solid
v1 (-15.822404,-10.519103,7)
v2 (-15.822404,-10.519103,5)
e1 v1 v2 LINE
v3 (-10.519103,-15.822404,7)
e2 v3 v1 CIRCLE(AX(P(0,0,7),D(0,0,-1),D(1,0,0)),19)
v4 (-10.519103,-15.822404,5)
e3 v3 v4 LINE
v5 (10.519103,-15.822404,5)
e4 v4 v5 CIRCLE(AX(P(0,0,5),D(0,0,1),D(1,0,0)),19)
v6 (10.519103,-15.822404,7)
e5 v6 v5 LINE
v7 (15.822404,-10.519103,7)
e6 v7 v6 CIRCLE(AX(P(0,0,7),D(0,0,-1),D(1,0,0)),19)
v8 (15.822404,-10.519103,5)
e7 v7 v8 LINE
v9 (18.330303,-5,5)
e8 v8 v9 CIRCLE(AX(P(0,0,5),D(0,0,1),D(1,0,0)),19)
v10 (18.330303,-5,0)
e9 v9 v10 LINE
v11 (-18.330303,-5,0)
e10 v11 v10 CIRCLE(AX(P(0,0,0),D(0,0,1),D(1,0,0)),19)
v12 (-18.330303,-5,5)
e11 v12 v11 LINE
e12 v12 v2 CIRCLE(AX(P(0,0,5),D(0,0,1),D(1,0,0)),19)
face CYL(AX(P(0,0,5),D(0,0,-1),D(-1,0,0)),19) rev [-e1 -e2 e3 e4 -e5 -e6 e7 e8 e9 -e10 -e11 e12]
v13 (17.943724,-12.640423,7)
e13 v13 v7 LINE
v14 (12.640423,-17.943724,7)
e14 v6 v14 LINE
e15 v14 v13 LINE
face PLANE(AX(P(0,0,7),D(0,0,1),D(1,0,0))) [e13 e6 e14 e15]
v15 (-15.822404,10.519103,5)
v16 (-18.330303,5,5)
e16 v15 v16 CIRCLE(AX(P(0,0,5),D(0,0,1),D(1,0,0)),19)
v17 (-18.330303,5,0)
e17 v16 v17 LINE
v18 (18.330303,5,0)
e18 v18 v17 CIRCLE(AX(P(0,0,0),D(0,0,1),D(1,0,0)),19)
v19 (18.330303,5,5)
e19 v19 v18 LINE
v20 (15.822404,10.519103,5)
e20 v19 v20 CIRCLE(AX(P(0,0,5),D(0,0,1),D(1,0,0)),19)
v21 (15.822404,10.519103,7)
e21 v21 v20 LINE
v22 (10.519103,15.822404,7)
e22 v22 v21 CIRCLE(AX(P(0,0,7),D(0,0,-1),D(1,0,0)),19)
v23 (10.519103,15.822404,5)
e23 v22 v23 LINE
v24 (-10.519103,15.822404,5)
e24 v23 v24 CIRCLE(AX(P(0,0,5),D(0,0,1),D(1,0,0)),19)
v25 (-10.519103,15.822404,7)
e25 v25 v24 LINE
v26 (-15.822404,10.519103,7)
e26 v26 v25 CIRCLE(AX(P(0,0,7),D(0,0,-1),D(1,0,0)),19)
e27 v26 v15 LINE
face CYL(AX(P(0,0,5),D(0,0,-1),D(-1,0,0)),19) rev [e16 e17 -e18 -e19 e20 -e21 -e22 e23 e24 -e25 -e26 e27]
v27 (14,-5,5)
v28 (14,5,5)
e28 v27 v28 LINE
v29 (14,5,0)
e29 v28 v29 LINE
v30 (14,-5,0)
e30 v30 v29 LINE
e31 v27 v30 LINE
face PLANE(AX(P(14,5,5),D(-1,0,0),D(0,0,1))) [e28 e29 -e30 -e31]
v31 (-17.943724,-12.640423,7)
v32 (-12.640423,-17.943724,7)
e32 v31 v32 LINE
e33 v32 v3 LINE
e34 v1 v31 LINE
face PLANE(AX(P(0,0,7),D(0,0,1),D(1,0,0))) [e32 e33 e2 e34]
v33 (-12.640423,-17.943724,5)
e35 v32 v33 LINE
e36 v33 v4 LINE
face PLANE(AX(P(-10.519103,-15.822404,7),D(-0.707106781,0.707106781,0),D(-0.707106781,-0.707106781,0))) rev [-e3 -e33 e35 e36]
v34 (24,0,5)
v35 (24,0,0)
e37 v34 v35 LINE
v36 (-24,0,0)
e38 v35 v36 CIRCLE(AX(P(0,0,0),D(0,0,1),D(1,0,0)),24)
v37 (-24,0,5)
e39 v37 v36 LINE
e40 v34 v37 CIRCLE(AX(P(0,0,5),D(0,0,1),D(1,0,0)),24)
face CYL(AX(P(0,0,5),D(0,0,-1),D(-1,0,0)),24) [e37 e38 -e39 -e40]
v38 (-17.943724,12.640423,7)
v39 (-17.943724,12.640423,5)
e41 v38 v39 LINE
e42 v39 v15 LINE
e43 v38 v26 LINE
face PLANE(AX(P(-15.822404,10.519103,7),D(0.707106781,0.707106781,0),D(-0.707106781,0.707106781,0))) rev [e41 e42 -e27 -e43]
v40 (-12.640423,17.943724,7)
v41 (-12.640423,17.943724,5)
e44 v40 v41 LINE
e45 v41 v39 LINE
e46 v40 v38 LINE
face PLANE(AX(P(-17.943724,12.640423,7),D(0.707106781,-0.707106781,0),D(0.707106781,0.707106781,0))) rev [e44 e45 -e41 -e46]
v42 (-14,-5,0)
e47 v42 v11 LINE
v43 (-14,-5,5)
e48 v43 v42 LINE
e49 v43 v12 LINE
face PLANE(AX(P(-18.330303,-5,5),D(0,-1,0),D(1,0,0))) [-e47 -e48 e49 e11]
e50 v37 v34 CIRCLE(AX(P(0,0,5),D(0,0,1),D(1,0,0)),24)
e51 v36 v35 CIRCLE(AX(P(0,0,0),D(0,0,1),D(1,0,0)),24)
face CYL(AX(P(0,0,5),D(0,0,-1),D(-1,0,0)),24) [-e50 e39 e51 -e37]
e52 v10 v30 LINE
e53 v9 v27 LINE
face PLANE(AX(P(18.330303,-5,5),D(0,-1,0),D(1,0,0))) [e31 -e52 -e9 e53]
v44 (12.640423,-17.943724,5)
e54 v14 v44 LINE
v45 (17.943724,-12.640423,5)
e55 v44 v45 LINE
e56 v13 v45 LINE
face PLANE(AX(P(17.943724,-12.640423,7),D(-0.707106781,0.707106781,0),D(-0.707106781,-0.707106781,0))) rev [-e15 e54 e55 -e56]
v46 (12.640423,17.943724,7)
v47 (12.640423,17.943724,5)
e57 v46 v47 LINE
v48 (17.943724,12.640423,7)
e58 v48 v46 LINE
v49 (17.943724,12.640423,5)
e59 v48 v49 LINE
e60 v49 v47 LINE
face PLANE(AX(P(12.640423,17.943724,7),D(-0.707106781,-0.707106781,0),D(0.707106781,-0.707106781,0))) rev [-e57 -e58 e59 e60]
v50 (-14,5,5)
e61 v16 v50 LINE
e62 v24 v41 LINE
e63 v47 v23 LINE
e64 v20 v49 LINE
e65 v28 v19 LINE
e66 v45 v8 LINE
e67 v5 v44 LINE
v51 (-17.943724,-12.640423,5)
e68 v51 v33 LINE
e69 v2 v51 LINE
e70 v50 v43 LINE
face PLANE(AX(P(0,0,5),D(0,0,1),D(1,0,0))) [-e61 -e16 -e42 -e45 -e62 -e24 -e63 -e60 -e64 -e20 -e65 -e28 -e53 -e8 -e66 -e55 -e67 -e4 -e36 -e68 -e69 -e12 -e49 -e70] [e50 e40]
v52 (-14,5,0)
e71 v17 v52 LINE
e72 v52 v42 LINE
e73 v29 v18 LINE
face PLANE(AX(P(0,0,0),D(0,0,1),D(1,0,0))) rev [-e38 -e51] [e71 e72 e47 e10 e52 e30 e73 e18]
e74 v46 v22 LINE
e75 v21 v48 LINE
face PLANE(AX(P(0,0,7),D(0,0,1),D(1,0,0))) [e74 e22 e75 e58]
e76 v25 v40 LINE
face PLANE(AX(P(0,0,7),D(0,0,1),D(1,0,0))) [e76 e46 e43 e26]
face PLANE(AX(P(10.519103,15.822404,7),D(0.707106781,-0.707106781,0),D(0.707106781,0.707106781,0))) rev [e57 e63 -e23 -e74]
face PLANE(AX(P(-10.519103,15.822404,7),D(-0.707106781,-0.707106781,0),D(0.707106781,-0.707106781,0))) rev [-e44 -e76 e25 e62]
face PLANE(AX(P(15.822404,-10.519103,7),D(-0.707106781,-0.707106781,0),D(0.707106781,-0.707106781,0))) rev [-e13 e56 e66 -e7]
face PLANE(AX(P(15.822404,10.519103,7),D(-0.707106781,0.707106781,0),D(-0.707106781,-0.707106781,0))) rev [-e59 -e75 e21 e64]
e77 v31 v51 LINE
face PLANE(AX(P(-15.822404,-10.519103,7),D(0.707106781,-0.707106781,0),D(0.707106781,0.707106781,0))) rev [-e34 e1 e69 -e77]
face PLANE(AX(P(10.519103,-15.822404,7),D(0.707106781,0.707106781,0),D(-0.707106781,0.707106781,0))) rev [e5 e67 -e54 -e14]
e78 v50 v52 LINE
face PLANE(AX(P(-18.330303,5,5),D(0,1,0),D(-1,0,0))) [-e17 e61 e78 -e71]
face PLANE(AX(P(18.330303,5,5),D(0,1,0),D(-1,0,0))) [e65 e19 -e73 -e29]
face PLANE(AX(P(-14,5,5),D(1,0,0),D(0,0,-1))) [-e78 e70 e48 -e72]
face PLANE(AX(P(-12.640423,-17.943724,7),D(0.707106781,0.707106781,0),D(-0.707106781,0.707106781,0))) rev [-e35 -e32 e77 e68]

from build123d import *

# Parameters (mm, degrees)
SKETCH_1_R      = 24
EXTRUDE_1_DEPTH = 5
EXTRUDE_2_DEPTH = 2


with BuildPart() as part:
    # 草图1 → 凸台-拉伸1 (new body)
    with BuildSketch(Plane.XY):
        Circle(SKETCH_1_R)
        with BuildLine():
            Line((-18.33030278, 5), (-14, 5))
            Line((-14, 5), (-14, -5))
            Line((-14, -5), (-18.33030278, -5))
            ThreePointArc((-18.33030278, -5), (0, -19), (18.33030278, -5))
            Line((18.33030278, -5), (14, -5))
            Line((14, -5), (14, 5))
            Line((14, 5), (18.33030278, 5))
            ThreePointArc((18.33030278, 5), (0, 19), (-18.33030278, 5))
        make_face(mode=Mode.SUBTRACT)
    extrude(amount=EXTRUDE_1_DEPTH)

    # 草图2 → 凸台-拉伸2 (add)
    with BuildSketch(Plane.XY.offset(5)):
        with BuildLine():
            Line((-15.822404015, 10.519103156), (-17.943724358, 12.640423499))
            Line((-17.943724358, 12.640423499), (-12.640423499, 17.943724358))
            Line((-12.640423499, 17.943724358), (-10.519103156, 15.822404015))
            ThreePointArc((-10.519103156, 15.822404015), (-13.435028843, 13.435028843), (-15.822404015, 10.519103156))
        make_face()
        with BuildLine():
            Line((10.519103156, 15.822404015), (12.640423499, 17.943724358))
            Line((12.640423499, 17.943724358), (17.943724358, 12.640423499))
            Line((17.943724358, 12.640423499), (15.822404015, 10.519103156))
            ThreePointArc((15.822404015, 10.519103156), (13.435028843, 13.435028843), (10.519103156, 15.822404015))
        make_face()
        with BuildLine():
            Line((15.822404015, -10.519103156), (17.943724358, -12.640423499))
            Line((17.943724358, -12.640423499), (12.640423499, -17.943724358))
            Line((12.640423499, -17.943724358), (10.519103156, -15.822404015))
            ThreePointArc((10.519103156, -15.822404015), (13.435028843, -13.435028843), (15.822404015, -10.519103156))
        make_face()
        with BuildLine():
            Line((-10.519103156, -15.822404015), (-12.640423499, -17.943724358))
            Line((-12.640423499, -17.943724358), (-17.943724358, -12.640423499))
            Line((-17.943724358, -12.640423499), (-15.822404015, -10.519103156))
            ThreePointArc((-15.822404015, -10.519103156), (-13.435028843, -13.435028843), (-10.519103156, -15.822404015))
        make_face()
    extrude(amount=EXTRUDE_2_DEPTH)


solid = part.part
